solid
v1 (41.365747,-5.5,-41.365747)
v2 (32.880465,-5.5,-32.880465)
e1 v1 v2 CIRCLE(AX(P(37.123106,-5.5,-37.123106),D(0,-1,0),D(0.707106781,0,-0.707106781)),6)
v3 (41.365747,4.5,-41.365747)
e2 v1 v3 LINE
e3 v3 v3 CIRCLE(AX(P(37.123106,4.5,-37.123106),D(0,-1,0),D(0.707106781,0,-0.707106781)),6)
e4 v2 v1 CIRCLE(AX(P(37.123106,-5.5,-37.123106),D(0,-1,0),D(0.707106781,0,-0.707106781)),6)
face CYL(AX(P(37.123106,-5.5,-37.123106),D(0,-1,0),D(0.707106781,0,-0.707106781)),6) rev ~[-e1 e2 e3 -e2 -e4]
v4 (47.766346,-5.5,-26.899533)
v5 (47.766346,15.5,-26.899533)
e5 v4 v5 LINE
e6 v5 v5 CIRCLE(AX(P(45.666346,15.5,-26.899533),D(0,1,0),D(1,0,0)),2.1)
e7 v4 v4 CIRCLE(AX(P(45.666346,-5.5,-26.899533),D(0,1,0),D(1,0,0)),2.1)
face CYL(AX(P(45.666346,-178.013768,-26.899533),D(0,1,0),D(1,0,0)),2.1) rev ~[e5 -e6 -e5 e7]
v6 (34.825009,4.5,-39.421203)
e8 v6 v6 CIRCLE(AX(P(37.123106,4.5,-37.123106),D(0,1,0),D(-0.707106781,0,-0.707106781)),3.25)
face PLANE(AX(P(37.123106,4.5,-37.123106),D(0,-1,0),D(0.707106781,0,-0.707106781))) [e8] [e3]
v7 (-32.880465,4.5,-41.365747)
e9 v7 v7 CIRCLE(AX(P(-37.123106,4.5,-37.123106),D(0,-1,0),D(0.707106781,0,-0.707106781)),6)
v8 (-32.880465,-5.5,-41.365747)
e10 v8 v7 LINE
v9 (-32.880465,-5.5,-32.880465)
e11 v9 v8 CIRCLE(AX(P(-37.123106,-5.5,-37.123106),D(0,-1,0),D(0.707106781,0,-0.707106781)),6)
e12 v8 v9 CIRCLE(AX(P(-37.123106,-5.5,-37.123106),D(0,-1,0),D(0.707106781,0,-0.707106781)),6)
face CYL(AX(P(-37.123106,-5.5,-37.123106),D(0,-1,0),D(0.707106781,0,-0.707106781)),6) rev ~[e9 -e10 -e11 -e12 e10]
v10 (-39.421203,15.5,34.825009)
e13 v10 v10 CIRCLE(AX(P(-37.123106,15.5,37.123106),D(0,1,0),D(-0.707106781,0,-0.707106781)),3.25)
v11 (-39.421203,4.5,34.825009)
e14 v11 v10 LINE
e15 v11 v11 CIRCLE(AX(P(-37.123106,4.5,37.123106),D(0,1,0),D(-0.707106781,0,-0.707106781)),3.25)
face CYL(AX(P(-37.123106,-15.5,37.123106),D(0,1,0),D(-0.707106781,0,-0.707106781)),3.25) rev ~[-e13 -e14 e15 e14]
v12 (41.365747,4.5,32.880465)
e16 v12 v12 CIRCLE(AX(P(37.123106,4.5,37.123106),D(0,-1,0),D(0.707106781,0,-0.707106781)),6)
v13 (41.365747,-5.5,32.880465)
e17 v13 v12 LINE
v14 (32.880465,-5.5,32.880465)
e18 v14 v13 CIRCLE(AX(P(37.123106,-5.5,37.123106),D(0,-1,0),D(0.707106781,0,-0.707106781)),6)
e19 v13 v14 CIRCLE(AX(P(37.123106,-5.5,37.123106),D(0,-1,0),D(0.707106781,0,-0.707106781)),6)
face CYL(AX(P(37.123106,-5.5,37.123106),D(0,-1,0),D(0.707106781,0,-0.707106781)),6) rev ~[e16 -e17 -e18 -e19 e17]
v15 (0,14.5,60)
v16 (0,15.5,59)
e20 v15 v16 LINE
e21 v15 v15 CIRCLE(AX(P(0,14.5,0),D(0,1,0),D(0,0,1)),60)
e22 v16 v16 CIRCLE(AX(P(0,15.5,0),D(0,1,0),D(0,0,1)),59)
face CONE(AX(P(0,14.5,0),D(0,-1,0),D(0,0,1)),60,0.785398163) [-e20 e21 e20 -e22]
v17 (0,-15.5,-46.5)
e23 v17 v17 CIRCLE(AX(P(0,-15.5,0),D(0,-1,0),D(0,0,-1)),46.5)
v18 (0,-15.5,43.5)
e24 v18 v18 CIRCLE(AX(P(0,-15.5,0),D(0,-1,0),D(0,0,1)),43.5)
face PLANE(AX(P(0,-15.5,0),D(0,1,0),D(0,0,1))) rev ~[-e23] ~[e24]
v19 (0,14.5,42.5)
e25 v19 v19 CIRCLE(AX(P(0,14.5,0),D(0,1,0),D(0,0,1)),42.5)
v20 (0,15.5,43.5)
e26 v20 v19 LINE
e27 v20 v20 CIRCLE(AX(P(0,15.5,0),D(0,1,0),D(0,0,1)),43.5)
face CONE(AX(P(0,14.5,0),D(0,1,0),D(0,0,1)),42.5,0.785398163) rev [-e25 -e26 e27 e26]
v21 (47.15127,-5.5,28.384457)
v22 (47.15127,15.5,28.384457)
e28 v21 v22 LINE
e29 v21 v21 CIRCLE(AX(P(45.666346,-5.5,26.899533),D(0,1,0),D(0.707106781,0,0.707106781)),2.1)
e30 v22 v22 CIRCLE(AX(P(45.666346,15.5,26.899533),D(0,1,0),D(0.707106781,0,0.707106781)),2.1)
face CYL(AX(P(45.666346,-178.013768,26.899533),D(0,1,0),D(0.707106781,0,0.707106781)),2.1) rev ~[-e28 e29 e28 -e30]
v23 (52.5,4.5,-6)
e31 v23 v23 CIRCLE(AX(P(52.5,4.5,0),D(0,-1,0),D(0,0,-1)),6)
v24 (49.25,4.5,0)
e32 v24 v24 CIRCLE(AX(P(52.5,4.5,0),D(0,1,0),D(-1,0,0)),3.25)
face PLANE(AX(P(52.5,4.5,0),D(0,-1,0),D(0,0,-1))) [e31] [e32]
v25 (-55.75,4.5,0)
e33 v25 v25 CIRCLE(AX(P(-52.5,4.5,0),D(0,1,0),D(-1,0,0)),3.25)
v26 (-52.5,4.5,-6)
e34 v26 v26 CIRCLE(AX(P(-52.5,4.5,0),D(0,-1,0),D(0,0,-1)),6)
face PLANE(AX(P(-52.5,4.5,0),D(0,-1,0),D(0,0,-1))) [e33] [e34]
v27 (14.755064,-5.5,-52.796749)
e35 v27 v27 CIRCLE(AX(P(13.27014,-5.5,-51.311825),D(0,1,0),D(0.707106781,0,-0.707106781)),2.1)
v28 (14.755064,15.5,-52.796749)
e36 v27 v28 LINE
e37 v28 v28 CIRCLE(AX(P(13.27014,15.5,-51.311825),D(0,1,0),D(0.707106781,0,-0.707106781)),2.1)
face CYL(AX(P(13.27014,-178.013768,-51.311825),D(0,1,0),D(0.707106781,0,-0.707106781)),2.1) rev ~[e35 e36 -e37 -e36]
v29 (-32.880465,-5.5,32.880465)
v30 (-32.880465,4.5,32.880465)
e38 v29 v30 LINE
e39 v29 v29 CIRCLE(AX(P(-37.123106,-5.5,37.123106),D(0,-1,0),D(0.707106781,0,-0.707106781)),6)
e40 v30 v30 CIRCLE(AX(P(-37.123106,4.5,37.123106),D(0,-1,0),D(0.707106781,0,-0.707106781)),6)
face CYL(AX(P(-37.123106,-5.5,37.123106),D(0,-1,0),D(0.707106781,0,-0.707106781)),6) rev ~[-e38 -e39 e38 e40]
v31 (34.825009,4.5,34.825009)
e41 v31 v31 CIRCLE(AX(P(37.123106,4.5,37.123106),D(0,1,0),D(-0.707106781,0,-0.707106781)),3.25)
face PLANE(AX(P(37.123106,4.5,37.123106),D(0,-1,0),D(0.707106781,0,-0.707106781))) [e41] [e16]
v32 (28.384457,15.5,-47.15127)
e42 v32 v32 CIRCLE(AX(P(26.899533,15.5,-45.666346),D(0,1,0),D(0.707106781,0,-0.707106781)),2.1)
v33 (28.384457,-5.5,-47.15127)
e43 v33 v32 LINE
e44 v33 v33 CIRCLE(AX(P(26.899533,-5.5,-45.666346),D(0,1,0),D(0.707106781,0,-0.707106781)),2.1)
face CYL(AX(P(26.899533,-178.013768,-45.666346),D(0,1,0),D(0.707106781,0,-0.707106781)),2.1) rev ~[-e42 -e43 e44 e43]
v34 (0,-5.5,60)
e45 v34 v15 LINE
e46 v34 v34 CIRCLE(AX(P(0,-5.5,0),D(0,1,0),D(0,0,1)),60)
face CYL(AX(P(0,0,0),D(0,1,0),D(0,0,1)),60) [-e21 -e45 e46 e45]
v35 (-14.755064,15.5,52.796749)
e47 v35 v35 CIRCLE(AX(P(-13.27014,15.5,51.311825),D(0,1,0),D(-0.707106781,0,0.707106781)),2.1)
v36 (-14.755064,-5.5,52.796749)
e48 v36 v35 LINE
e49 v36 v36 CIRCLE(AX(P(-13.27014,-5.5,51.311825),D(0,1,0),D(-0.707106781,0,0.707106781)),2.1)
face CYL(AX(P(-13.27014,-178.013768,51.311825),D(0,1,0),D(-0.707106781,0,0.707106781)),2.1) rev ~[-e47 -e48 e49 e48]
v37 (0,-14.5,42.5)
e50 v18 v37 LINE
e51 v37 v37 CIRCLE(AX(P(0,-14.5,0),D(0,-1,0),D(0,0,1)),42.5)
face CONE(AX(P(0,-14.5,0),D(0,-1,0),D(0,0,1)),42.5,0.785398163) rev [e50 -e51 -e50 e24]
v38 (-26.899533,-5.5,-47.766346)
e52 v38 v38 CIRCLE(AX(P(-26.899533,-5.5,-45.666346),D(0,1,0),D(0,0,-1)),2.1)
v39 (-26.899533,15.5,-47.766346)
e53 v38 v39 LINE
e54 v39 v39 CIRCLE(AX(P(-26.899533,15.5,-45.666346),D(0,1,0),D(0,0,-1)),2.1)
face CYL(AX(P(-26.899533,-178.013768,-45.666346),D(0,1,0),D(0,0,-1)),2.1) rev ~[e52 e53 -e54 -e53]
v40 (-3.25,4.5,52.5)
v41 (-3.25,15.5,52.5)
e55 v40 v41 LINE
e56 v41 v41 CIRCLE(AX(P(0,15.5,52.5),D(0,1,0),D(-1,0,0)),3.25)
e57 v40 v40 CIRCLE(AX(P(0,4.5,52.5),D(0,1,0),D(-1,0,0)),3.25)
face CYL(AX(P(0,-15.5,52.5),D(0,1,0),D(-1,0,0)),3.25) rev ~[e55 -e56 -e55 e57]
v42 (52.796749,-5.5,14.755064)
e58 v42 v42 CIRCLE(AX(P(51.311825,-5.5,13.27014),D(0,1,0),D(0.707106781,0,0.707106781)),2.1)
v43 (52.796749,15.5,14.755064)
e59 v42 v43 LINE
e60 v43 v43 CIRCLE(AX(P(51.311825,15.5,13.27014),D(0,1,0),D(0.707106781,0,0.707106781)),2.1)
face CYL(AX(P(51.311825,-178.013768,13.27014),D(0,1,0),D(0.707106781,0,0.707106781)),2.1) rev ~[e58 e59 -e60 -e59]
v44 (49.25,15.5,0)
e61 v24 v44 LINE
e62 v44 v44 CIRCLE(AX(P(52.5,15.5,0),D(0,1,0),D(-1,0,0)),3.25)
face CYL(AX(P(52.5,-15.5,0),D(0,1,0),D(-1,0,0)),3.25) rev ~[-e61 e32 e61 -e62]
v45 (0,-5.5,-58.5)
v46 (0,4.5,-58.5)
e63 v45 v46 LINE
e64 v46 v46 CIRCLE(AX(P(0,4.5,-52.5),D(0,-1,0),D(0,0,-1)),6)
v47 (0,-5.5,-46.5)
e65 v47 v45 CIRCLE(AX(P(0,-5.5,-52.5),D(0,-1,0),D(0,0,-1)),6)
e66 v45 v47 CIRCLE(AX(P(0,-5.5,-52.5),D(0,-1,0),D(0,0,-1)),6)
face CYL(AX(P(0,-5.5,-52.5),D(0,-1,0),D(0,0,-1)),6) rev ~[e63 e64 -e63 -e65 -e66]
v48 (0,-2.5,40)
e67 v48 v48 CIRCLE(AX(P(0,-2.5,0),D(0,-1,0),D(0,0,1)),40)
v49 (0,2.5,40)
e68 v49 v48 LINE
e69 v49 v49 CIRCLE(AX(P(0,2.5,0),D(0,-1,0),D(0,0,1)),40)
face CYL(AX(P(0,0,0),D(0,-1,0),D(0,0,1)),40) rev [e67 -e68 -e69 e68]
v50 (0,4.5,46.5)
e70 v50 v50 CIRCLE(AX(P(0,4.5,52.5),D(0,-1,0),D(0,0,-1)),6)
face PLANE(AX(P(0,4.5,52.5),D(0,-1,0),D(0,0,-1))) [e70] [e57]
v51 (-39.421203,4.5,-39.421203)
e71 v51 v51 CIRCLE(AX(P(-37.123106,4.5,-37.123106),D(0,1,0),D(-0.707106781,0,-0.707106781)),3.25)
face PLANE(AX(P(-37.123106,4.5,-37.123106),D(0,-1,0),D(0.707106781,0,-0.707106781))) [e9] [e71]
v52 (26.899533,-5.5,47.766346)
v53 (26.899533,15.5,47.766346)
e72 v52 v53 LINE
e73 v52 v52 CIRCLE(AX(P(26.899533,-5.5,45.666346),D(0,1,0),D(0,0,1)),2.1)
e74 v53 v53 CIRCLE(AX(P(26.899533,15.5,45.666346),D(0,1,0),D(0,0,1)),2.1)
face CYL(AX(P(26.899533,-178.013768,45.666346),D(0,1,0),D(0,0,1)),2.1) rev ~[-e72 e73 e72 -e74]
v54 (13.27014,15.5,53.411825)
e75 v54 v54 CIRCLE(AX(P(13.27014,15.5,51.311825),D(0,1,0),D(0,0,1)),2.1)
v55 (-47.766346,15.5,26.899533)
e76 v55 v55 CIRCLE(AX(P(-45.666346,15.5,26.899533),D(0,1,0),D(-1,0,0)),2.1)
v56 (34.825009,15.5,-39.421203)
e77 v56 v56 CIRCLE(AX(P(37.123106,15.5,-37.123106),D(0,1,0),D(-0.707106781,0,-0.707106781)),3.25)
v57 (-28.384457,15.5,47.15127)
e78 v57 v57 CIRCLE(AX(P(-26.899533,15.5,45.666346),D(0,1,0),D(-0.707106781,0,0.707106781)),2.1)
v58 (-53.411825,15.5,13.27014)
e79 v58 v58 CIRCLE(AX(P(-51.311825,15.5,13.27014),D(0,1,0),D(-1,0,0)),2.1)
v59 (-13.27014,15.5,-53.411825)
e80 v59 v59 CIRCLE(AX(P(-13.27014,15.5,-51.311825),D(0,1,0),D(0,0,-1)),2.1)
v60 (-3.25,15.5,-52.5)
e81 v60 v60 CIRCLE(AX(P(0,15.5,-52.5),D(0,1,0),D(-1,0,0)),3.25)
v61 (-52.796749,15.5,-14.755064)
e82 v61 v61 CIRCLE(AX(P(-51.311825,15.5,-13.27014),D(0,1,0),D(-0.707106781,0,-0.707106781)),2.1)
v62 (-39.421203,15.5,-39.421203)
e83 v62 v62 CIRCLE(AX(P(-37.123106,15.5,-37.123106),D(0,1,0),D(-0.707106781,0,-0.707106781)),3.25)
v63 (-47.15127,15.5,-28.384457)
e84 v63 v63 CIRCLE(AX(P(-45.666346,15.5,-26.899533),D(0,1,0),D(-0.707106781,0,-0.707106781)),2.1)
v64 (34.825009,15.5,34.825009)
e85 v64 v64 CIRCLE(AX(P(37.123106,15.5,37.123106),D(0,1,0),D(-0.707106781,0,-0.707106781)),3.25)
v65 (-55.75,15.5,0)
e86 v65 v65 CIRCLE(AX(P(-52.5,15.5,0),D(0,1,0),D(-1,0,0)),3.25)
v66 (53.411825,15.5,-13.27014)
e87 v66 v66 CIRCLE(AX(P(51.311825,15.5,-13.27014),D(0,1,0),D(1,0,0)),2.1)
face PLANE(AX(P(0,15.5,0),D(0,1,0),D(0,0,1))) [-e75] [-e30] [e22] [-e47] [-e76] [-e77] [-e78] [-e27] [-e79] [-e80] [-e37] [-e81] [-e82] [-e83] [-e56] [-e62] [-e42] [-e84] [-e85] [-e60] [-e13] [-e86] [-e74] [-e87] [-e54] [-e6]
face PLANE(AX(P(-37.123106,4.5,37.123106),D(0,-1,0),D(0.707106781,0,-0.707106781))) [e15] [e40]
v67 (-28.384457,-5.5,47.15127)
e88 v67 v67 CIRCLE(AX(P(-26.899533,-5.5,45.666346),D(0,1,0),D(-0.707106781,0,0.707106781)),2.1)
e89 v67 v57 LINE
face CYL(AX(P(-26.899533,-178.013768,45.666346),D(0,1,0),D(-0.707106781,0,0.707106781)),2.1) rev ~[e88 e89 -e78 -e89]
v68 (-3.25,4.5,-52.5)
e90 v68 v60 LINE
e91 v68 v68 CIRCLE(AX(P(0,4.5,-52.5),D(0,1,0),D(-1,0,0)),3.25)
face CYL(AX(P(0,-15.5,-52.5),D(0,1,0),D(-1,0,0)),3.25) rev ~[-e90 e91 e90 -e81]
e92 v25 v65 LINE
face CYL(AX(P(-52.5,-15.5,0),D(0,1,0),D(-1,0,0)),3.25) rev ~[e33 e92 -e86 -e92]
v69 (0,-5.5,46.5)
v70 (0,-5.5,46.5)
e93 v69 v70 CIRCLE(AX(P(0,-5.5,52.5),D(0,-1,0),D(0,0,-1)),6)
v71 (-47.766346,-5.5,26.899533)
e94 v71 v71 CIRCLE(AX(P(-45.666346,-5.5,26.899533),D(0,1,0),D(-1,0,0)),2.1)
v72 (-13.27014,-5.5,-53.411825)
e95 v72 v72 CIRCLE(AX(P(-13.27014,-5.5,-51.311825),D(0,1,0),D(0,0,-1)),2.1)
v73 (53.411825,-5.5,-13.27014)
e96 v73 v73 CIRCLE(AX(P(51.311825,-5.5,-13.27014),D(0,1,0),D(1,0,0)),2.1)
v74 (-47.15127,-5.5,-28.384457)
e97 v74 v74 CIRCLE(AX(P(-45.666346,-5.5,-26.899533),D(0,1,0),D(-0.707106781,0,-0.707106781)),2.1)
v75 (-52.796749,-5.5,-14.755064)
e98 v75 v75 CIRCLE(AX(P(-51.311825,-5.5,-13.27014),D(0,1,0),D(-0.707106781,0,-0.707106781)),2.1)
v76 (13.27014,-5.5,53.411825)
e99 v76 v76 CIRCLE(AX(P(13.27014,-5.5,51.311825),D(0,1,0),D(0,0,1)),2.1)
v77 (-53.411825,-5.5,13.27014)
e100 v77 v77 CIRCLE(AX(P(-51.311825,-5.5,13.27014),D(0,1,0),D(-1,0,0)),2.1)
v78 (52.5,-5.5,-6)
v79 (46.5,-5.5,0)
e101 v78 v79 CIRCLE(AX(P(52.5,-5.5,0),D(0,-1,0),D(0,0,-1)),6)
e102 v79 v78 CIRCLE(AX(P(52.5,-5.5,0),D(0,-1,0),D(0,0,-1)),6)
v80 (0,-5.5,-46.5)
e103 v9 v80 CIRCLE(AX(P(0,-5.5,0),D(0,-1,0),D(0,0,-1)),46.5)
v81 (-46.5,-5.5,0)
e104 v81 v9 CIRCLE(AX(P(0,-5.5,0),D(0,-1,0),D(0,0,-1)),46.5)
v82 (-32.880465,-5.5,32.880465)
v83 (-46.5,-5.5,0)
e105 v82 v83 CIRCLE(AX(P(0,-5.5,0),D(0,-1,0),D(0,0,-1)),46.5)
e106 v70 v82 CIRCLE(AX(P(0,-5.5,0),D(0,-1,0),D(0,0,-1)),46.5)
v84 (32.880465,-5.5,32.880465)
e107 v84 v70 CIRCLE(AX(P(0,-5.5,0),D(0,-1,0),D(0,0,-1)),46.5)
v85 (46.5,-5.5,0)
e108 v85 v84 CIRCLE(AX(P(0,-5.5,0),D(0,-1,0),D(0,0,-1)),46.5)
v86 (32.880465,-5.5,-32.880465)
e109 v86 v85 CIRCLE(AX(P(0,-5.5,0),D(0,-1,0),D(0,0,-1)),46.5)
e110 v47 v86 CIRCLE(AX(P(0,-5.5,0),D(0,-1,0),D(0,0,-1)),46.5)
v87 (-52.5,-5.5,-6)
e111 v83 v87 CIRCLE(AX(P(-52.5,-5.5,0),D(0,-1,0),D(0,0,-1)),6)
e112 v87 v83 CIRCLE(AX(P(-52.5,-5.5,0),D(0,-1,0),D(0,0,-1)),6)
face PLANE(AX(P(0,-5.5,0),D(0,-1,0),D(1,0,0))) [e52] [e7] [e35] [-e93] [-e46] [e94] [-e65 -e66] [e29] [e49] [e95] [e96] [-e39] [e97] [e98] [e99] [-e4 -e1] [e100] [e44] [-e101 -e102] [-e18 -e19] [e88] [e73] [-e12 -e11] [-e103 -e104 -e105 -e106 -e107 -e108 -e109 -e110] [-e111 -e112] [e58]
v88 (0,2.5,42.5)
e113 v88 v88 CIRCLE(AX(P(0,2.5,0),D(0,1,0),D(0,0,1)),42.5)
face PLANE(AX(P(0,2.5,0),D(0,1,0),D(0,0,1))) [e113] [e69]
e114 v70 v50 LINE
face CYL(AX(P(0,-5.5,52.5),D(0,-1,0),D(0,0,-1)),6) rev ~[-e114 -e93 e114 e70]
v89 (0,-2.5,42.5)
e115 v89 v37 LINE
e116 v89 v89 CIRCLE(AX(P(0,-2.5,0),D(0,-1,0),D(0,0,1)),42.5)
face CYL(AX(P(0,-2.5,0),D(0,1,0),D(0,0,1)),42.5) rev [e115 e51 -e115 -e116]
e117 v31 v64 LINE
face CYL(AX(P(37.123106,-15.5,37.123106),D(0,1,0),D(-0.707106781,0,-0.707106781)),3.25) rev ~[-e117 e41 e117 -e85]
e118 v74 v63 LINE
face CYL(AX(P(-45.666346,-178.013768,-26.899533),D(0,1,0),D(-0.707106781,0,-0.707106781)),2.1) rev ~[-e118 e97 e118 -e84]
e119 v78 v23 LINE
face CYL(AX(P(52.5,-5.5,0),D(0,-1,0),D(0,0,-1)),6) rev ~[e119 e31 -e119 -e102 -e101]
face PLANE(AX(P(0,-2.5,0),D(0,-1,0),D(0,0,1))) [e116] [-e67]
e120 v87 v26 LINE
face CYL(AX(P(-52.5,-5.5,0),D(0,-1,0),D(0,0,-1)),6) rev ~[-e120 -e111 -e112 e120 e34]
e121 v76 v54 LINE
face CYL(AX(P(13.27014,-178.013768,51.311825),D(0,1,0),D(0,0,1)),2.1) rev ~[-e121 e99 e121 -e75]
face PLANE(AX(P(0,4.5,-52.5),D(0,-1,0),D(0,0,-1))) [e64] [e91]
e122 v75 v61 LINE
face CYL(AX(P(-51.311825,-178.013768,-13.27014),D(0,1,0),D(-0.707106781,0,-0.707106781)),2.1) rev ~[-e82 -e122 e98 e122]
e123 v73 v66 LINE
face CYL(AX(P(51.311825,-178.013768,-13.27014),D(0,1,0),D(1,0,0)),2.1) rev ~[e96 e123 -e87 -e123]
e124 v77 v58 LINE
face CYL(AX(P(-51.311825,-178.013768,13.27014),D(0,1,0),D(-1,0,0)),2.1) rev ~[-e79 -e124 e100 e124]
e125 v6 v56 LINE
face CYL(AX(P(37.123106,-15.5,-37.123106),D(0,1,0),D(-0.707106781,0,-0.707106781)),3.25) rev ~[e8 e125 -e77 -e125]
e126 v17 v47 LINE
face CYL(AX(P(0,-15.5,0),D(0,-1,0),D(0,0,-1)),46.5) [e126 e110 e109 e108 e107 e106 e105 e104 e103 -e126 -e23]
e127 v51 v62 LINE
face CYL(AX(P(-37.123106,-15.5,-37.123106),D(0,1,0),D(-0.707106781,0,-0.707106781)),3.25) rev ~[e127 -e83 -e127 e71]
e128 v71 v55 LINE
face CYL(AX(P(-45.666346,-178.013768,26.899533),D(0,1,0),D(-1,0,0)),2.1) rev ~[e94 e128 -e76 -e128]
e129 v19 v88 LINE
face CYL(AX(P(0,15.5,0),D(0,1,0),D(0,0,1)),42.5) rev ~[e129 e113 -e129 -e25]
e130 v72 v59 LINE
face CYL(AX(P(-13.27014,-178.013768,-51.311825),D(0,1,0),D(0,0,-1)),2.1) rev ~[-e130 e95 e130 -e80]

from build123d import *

# Parameters (mm, degrees)
SKETCH_1_R                = 60
SKETCH_1_R_2              = 40
EXTRUDE_1_DEPTH           = 15.5
CHAMFER_1_SIZE            = 1
HOLE_WIZARD_1_D           = 6.5
HOLE_WIZARD_1_CBORE_D     = 11
HOLE_WIZARD_1_CBORE_DEPTH = 6.8
SKETCH_7_R                = 42.5
CUT_EXTRUDE_2_DEPTH       = 13
CUT_EXTRUDE_START         = -13
SKETCH_8_R                = 42.5
CUT_EXTRUDE_3_DEPTH       = 13
SKETCH_9_R                = 67.994168063
SKETCH_9_R_2              = 46.5
CUT_EXTRUDE_4_DEPTH       = 10
HOLE_WIZARD_M5_1_D        = 4.2
PATTERN_CIRCULAR_1_COUNT  = 8
SKETCH_10_R               = 6
CUT_EXTRUDE_5_DEPTH       = 10
PATTERN_CIRCULAR_2_COUNT  = 2
PATTERN_CIRCULAR_2_ANGLE  = 45
PATTERN_CIRCULAR_3_COUNT  = 2
PATTERN_CIRCULAR_3_ANGLE  = 45
CHAMFER_2_SIZE            = 1


with BuildPart() as part:
    # 草图1 → 凸台-拉伸1 (new, symmetric)
    with BuildSketch(Plane(origin=(0, 0, 0), x_dir=(1, 0, 0), z_dir=(0, 1, 0))):
        with Locations(Location((0, 0, 0), (0, 0, 270))):
            Circle(SKETCH_1_R)
        with Locations(Location((0, 0, 0), (0, 0, 270))):
            Circle(SKETCH_1_R_2, mode=Mode.SUBTRACT)
    extrude(amount=EXTRUDE_1_DEPTH, both=True)

    # 倒角1
    chamfer_1_edges = [part.edges().sort_by_distance(p)[0] for p in [
        (0, -15.5, -60),
        (0, 15.5, -60),
        (0, -15.5, -40),
        (0, 15.5, -40),
    ]]
    chamfer(chamfer_1_edges, length=CHAMFER_1_SIZE)

    # 打孔尺寸根据内六角圆柱头螺钉的类型1 (through all)
    with Locations(Plane(origin=(-41.126423616, -15.5, 15.006070464), x_dir=(1, 0, 0), z_dir=(0, -1, 0))):
        with Locations((-11.373576384, -15.006070464), (93.626423616, -15.006070464), (41.126423616, -67.506070464), (41.126423616, 37.493929536)):
            hole_wizard_1 = CounterBoreHole(HOLE_WIZARD_1_D / 2, HOLE_WIZARD_1_CBORE_D / 2, HOLE_WIZARD_1_CBORE_DEPTH)

    # 草图7 → 切除-拉伸2 (cut)
    with BuildSketch(Plane(origin=(0, 15.5, 0), x_dir=(1, 0, 0), z_dir=(0, 1, 0))):
        with Locations(Location((0, 0, 0), (0, 0, 270))):
            Circle(SKETCH_7_R)
    extrude(amount=-CUT_EXTRUDE_2_DEPTH, mode=Mode.SUBTRACT)

    # 草图8 → 切除-拉伸3 (cut)
    with BuildSketch(Plane.XZ.offset(15.5).offset(CUT_EXTRUDE_START)):
        with Locations(Location((0, 0, 0), (0, 0, 90))):
            Circle(SKETCH_8_R)
    extrude(amount=CUT_EXTRUDE_3_DEPTH, mode=Mode.SUBTRACT)

    # 草图9 → 切除-拉伸4 (cut)
    with BuildSketch(Plane.XZ.offset(15.5)):
        Circle(SKETCH_9_R)
        with Locations(Location((0, 0, 0), (0, 0, 270))):
            Circle(SKETCH_9_R_2, mode=Mode.SUBTRACT)
    extrude(amount=-CUT_EXTRUDE_4_DEPTH, mode=Mode.SUBTRACT)

    # M5 螺纹孔1 (through all)
    with Locations(Plane(origin=(22.072004657, -5.5, -2.458986171), x_dir=(-1, 0, 0), z_dir=(0, -1, 0))):
        with Locations((-23.594340847, 24.440547066), (-29.239820284, 10.811154044)):
            hole_wizard_m5_1 = Hole(HOLE_WIZARD_M5_1_D / 2)

    # 阵列(圆周)1: M5 螺纹孔1 ×8 about axis
    pattern_circular_1_axis = Axis((0, 0, 0), (0, 1, 0))
    for i in range(1, PATTERN_CIRCULAR_1_COUNT):
        add(hole_wizard_m5_1.rotate(pattern_circular_1_axis, i * 360 / PATTERN_CIRCULAR_1_COUNT), mode=Mode.SUBTRACT)

    # 草图10 → 切除-拉伸5 (cut)
    with BuildSketch(Plane.XZ.offset(5.5)):
        with Locations(Location((0, -52.5, 0), (0, 0, 270))):
            Circle(SKETCH_10_R)
        with Locations(Location((52.5, 0, 0), (0, 0, 270))):
            Circle(SKETCH_10_R)
        with Locations(Location((0, 52.5, 0), (0, 0, 270))):
            Circle(SKETCH_10_R)
        with Locations(Location((-52.5, 0, 0), (0, 0, 270))):
            Circle(SKETCH_10_R)
    cut_extrude_5 = extrude(amount=-CUT_EXTRUDE_5_DEPTH, mode=Mode.SUBTRACT)

    # 阵列(圆周)2: 打孔尺寸根据内六角圆柱头螺钉的类型1 ×2 about axis
    pattern_circular_2_axis = Axis((0, 0, 0), (0, -1, 0))
    for i in range(1, PATTERN_CIRCULAR_2_COUNT):
        add(hole_wizard_1.rotate(pattern_circular_2_axis, i * PATTERN_CIRCULAR_2_ANGLE / (PATTERN_CIRCULAR_2_COUNT - 1)), mode=Mode.SUBTRACT)

    # 阵列(圆周)3: 切除-拉伸5 ×2 about axis
    pattern_circular_3_axis = Axis((0, 0, 0), (0, -1, 0))
    for i in range(1, PATTERN_CIRCULAR_3_COUNT):
        add(cut_extrude_5.rotate(pattern_circular_3_axis, i * PATTERN_CIRCULAR_3_ANGLE / (PATTERN_CIRCULAR_3_COUNT - 1)), mode=Mode.SUBTRACT)

    # 倒角2
    chamfer_2_edges = [part.edges().sort_by_distance(p)[0] for p in [
        (0, 15.5, -42.5),
        (0, -15.5, -42.5),
    ]]
    chamfer(chamfer_2_edges, length=CHAMFER_2_SIZE)


solid = part.part
